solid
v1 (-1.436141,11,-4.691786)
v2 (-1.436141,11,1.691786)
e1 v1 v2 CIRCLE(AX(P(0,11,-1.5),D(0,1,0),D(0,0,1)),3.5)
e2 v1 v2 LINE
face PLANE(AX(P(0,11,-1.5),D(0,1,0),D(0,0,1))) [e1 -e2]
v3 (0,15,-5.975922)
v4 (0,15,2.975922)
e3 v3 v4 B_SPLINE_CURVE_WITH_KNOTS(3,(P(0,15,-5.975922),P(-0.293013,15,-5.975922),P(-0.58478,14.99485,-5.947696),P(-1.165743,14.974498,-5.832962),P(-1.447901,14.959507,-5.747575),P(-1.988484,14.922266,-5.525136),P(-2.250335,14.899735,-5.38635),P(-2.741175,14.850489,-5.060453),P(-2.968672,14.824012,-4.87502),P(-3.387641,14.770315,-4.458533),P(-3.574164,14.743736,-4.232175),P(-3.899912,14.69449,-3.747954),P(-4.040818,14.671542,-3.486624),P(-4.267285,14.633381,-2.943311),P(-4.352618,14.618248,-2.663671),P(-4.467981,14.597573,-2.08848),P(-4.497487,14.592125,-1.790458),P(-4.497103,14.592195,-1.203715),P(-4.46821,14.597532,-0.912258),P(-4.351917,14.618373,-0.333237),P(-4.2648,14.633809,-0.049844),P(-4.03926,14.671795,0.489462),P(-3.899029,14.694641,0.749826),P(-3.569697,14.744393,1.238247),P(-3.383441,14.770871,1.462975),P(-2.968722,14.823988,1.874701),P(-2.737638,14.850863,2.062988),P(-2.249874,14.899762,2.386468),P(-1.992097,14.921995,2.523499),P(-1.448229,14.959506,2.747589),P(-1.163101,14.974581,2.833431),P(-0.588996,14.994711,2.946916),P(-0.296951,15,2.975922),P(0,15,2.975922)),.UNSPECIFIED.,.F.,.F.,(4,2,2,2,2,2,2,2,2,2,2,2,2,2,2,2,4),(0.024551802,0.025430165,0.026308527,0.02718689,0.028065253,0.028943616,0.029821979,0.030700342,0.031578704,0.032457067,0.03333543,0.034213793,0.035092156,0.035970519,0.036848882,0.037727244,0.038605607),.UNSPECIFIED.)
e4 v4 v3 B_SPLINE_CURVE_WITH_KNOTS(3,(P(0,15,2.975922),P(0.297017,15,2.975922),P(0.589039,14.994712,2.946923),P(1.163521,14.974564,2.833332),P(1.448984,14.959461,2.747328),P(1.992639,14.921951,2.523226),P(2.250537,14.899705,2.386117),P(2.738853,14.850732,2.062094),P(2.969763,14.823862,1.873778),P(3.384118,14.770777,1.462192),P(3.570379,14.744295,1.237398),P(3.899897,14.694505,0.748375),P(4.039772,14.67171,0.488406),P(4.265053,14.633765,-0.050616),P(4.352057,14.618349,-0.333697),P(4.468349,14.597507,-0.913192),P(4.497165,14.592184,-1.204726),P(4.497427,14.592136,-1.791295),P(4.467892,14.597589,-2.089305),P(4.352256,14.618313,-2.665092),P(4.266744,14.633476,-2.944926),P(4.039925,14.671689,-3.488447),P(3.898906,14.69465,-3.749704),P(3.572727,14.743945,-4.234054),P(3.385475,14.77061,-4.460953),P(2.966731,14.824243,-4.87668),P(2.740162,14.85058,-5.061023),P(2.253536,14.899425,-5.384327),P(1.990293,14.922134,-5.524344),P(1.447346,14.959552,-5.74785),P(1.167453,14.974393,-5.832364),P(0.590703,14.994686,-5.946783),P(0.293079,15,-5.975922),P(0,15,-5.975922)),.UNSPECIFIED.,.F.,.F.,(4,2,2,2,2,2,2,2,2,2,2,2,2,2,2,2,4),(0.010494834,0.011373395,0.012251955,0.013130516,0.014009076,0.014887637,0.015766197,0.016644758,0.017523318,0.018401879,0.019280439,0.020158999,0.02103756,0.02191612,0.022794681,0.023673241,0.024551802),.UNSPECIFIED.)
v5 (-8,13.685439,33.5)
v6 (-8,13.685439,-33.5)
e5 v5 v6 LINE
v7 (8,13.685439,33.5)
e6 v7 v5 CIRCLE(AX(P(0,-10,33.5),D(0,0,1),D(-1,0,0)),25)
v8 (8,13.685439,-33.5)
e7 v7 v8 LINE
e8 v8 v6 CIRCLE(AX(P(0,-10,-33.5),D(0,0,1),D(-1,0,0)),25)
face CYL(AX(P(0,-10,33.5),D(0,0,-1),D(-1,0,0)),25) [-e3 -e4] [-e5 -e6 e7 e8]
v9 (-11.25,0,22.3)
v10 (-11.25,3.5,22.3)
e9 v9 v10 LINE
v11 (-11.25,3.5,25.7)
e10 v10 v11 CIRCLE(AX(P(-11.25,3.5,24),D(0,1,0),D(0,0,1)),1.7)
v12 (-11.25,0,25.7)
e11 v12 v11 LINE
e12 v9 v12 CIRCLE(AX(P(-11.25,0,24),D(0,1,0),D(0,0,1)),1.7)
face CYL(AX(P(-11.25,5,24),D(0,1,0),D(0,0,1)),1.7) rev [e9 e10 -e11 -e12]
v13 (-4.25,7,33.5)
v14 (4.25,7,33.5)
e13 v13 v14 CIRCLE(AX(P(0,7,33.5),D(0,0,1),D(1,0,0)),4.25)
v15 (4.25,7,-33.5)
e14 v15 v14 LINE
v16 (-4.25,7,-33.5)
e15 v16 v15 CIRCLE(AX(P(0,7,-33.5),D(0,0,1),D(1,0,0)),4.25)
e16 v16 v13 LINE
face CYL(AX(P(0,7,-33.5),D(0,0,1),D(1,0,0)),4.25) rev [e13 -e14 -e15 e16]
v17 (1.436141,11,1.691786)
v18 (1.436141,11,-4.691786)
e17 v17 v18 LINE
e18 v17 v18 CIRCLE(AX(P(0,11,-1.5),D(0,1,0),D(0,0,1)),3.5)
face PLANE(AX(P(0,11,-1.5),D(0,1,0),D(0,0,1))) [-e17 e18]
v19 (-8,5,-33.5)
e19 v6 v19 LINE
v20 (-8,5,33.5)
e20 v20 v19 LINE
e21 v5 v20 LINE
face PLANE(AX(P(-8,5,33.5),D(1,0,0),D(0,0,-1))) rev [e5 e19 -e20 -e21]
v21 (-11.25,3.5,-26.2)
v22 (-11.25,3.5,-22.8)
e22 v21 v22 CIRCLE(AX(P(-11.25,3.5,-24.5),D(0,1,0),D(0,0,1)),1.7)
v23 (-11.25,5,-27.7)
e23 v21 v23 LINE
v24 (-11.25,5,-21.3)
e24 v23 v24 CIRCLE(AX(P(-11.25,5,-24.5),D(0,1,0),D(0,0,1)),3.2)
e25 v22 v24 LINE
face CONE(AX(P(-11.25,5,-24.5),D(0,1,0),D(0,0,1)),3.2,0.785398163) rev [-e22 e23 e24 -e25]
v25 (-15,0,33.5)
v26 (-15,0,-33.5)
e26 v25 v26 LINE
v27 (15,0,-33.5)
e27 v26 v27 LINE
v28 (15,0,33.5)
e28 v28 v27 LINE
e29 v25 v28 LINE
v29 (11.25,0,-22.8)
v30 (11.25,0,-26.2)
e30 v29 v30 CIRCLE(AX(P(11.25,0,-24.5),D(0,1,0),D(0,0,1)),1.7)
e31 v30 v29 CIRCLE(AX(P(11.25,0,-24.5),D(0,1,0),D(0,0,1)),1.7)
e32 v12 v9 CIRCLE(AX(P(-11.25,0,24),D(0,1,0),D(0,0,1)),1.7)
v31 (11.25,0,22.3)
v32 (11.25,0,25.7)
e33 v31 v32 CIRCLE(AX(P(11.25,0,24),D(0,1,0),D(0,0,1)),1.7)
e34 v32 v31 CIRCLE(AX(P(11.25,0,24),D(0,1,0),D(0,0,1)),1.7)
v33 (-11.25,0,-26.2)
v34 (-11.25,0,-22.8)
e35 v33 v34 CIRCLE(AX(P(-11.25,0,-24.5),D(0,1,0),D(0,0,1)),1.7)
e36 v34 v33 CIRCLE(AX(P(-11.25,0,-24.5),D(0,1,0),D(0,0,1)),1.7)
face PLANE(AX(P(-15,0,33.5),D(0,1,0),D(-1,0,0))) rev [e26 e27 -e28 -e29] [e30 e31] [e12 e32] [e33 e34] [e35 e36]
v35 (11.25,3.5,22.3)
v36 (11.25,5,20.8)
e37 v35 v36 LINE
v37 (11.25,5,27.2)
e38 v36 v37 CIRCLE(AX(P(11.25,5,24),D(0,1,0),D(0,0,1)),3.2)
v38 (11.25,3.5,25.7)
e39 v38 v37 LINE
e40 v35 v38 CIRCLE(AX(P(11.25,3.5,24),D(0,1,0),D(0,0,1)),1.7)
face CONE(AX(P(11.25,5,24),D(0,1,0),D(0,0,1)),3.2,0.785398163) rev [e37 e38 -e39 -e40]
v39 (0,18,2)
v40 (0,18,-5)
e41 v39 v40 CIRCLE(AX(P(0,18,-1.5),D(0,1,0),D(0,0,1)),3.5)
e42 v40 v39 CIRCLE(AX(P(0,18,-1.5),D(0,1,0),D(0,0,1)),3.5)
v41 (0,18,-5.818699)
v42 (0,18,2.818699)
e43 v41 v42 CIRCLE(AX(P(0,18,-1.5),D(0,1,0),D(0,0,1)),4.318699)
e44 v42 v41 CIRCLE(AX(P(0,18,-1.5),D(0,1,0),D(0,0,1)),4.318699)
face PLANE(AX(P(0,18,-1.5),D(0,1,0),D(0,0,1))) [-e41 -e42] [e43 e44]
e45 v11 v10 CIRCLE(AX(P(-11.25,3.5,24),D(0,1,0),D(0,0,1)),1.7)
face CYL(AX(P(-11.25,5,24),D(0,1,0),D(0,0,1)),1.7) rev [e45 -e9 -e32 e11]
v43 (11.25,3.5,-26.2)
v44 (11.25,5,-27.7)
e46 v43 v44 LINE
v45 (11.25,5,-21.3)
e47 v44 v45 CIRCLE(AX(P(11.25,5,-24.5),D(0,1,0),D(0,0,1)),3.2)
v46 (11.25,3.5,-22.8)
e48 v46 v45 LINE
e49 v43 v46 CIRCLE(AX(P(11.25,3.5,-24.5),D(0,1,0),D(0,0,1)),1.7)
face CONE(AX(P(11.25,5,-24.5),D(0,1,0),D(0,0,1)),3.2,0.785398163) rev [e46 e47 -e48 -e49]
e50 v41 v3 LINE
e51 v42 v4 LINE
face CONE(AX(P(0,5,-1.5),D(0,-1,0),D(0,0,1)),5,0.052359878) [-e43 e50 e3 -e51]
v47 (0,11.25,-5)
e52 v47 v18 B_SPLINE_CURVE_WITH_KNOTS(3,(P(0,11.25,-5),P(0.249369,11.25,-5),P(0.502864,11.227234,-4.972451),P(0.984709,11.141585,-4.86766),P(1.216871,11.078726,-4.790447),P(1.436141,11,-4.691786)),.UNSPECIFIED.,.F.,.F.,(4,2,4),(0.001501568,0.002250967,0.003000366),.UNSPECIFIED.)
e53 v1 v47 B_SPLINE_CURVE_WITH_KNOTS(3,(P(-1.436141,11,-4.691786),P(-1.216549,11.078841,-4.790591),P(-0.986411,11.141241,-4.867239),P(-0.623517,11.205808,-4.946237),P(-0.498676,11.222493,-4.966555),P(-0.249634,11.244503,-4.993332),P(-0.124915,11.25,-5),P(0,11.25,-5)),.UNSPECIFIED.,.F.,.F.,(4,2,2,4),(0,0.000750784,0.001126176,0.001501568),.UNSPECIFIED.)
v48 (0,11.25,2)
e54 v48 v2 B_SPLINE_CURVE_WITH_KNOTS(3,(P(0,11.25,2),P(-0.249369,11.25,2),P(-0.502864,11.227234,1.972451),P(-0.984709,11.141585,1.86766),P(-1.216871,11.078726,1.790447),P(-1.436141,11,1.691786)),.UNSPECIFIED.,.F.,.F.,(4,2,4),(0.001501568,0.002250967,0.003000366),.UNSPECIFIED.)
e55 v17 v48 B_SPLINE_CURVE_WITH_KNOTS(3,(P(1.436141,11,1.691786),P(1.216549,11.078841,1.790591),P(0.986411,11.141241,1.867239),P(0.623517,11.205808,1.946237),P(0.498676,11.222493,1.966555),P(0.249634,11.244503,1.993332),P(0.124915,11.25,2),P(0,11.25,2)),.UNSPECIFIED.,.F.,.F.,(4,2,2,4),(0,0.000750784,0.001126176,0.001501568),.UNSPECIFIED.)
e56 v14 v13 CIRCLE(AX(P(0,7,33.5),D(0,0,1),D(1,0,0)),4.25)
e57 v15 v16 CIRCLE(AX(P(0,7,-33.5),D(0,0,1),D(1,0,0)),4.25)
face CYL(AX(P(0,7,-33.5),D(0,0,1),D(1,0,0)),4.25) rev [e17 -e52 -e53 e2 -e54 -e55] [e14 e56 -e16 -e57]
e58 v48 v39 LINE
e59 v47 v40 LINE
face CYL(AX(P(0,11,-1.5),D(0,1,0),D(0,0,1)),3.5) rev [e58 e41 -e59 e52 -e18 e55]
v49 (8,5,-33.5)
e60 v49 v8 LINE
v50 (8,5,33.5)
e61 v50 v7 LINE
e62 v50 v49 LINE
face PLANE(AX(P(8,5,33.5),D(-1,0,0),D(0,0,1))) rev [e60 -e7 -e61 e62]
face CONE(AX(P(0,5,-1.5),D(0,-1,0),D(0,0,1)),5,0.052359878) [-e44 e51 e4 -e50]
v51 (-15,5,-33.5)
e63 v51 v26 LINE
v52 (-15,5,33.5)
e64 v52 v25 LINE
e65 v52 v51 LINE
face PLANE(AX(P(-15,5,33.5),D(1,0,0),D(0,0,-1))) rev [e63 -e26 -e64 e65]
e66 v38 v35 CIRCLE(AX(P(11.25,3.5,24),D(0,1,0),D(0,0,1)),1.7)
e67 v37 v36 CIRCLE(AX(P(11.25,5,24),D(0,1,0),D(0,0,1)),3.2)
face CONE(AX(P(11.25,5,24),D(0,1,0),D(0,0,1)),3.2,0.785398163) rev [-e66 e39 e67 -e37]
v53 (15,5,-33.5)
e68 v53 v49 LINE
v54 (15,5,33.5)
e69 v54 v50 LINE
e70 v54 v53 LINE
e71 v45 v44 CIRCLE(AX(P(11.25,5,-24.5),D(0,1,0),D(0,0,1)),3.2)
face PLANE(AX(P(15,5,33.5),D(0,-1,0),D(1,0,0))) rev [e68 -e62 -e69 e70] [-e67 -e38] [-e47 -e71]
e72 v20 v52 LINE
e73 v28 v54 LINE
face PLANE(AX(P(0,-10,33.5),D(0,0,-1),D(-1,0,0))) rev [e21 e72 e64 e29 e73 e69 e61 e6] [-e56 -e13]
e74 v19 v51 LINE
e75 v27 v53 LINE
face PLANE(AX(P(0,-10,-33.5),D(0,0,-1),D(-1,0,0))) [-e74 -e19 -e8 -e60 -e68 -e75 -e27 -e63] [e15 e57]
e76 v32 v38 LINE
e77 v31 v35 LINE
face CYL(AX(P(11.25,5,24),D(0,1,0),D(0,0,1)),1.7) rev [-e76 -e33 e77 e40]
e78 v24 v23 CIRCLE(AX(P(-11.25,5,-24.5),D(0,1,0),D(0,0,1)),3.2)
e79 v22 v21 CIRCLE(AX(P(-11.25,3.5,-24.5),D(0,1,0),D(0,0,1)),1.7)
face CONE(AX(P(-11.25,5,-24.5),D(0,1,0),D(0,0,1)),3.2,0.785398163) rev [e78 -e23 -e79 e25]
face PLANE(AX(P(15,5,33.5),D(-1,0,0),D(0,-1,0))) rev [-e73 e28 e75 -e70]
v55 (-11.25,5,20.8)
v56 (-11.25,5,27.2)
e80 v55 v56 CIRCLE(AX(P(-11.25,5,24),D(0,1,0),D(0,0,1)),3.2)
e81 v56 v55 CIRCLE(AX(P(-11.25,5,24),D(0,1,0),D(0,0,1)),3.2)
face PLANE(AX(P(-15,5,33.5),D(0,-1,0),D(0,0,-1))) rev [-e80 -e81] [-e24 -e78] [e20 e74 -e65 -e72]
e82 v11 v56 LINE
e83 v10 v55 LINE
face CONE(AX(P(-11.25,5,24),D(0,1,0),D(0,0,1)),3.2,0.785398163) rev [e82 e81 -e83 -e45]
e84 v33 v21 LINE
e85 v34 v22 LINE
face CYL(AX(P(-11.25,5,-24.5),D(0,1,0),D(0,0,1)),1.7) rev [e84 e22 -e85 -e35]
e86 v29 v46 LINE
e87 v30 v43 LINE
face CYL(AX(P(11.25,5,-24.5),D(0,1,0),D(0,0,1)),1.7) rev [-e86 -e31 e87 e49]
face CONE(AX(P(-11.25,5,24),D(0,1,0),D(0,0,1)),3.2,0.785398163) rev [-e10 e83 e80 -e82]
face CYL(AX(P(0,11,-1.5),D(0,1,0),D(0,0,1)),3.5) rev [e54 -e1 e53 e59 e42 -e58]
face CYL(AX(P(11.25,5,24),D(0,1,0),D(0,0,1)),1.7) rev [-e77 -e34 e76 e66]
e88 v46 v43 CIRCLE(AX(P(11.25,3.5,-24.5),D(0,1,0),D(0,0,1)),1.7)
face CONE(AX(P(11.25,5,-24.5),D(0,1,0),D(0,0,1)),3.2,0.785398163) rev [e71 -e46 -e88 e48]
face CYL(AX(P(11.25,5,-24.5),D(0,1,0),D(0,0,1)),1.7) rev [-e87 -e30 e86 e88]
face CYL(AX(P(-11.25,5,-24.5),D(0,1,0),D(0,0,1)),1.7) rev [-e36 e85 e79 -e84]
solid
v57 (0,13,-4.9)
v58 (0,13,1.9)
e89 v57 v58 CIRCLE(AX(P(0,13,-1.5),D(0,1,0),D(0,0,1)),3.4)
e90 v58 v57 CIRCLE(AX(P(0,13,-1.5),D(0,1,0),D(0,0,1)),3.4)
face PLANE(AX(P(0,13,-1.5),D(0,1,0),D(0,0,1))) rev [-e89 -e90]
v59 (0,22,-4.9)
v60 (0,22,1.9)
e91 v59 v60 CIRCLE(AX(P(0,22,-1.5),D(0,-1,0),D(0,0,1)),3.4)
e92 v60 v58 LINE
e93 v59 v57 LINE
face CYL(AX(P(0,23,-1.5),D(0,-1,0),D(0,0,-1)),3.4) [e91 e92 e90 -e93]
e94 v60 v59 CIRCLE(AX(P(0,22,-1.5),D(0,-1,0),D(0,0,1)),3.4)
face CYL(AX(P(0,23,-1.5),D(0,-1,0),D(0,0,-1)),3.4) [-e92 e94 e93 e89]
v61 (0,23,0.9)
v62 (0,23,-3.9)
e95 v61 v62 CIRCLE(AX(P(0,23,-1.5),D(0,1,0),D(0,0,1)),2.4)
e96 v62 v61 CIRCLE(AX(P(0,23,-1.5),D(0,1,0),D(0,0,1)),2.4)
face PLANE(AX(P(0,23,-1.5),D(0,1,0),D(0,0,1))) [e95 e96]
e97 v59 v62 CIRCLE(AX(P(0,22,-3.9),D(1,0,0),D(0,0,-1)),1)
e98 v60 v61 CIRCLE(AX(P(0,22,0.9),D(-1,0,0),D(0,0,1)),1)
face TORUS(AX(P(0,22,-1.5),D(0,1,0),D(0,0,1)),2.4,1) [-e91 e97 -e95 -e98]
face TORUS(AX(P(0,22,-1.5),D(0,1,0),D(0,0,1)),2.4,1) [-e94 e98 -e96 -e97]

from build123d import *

# Parameters (mm, degrees)
EXTRUDE_1_DEPTH           = 33.5
HOLE_WIZARD_1_D           = 3.4
HOLE_WIZARD_1_CSINK_D     = 6.4
HOLE_WIZARD_1_CSINK_ANGLE = 90
SKETCH_4_R                = 5
EXTRUDE_2_DEPTH           = 13
EXTRUDE_2_TAPER           = 3
SKETCH_6_R                = 3.5
CUT_EXTRUDE_2_DEPTH       = 7
SKETCH_5_R                = 4.25
CUT_EXTRUDE_1_DEPTH       = 71.978870215
SKETCH_7_R                = 3.4
EXTRUDE_3_DEPTH           = 5
FILLET_1_R                = 1


with BuildPart() as part:
    # 草图1 → 凸台-拉伸1 (new, symmetric)
    with BuildSketch(Plane.XY):
        with BuildLine():
            Line((-15, 5), (-8, 5))
            Line((-8, 5), (-8, 13.685438565))
            ThreePointArc((-8, 13.685438565), (0, 15), (8, 13.685438565))
            Line((8, 13.685438565), (8, 5))
            Line((8, 5), (15, 5))
            Line((15, 5), (15, 0))
            Line((15, 0), (-15, 0))
            Line((-15, 0), (-15, 5))
        make_face()
    extrude(amount=EXTRUDE_1_DEPTH, both=True)

    # 打孔尺寸开槽半沉头螺钉的类型1 (through all)
    with Locations(Plane(origin=(0, 5, 0), x_dir=(1, 0, 0), z_dir=(0, 1, 0))):
        with Locations((-11.25, 24.5), (-11.25, -24), (11.25, -24), (11.25, 24.5)):
            CounterSinkHole(HOLE_WIZARD_1_D / 2, HOLE_WIZARD_1_CSINK_D / 2, counter_sink_angle=HOLE_WIZARD_1_CSINK_ANGLE)

    # 草图4 → 凸台-拉伸2 (add)
    with BuildSketch(Plane(origin=(0, 5, 0), x_dir=(1, 0, 0), z_dir=(0, 1, 0))):
        with Locations((0, 1.5)):
            Circle(SKETCH_4_R)
    extrude(amount=EXTRUDE_2_DEPTH, taper=EXTRUDE_2_TAPER)

    # 草图6 → 切除-拉伸2 (cut)
    with BuildSketch(Plane(origin=(0, 18, 0), x_dir=(1, 0, 0), z_dir=(0, 1, 0))):
        with Locations(Location((0, 1.5, 0), (0, 0, 270))):
            Circle(SKETCH_6_R)
    extrude(amount=-CUT_EXTRUDE_2_DEPTH, mode=Mode.SUBTRACT)

    # 草图5 → 切除-拉伸1 (cut, through all)
    with BuildSketch(Plane.XY.offset(33.5)):
        with Locations((0, 7)):
            Circle(SKETCH_5_R)
    extrude(amount=-CUT_EXTRUDE_1_DEPTH, mode=Mode.SUBTRACT)


with BuildPart() as body_2:
    # 草图7 → 凸台-拉伸3 (new, symmetric)
    with BuildSketch(Plane(origin=(0, 18, 0), x_dir=(1, 0, 0), z_dir=(0, 1, 0))):
        with Locations(Location((0, 1.5, 0), (0, 0, 270))):
            Circle(SKETCH_7_R)
    extrude(amount=EXTRUDE_3_DEPTH, both=True)

    # 圆角1
    fillet_1_edges = [body_2.edges().sort_by_distance(p)[0] for p in [
        (0, 23, -4.9),
    ]]
    fillet(fillet_1_edges, radius=FILLET_1_R)


solid = Compound([part.part, body_2.part])
